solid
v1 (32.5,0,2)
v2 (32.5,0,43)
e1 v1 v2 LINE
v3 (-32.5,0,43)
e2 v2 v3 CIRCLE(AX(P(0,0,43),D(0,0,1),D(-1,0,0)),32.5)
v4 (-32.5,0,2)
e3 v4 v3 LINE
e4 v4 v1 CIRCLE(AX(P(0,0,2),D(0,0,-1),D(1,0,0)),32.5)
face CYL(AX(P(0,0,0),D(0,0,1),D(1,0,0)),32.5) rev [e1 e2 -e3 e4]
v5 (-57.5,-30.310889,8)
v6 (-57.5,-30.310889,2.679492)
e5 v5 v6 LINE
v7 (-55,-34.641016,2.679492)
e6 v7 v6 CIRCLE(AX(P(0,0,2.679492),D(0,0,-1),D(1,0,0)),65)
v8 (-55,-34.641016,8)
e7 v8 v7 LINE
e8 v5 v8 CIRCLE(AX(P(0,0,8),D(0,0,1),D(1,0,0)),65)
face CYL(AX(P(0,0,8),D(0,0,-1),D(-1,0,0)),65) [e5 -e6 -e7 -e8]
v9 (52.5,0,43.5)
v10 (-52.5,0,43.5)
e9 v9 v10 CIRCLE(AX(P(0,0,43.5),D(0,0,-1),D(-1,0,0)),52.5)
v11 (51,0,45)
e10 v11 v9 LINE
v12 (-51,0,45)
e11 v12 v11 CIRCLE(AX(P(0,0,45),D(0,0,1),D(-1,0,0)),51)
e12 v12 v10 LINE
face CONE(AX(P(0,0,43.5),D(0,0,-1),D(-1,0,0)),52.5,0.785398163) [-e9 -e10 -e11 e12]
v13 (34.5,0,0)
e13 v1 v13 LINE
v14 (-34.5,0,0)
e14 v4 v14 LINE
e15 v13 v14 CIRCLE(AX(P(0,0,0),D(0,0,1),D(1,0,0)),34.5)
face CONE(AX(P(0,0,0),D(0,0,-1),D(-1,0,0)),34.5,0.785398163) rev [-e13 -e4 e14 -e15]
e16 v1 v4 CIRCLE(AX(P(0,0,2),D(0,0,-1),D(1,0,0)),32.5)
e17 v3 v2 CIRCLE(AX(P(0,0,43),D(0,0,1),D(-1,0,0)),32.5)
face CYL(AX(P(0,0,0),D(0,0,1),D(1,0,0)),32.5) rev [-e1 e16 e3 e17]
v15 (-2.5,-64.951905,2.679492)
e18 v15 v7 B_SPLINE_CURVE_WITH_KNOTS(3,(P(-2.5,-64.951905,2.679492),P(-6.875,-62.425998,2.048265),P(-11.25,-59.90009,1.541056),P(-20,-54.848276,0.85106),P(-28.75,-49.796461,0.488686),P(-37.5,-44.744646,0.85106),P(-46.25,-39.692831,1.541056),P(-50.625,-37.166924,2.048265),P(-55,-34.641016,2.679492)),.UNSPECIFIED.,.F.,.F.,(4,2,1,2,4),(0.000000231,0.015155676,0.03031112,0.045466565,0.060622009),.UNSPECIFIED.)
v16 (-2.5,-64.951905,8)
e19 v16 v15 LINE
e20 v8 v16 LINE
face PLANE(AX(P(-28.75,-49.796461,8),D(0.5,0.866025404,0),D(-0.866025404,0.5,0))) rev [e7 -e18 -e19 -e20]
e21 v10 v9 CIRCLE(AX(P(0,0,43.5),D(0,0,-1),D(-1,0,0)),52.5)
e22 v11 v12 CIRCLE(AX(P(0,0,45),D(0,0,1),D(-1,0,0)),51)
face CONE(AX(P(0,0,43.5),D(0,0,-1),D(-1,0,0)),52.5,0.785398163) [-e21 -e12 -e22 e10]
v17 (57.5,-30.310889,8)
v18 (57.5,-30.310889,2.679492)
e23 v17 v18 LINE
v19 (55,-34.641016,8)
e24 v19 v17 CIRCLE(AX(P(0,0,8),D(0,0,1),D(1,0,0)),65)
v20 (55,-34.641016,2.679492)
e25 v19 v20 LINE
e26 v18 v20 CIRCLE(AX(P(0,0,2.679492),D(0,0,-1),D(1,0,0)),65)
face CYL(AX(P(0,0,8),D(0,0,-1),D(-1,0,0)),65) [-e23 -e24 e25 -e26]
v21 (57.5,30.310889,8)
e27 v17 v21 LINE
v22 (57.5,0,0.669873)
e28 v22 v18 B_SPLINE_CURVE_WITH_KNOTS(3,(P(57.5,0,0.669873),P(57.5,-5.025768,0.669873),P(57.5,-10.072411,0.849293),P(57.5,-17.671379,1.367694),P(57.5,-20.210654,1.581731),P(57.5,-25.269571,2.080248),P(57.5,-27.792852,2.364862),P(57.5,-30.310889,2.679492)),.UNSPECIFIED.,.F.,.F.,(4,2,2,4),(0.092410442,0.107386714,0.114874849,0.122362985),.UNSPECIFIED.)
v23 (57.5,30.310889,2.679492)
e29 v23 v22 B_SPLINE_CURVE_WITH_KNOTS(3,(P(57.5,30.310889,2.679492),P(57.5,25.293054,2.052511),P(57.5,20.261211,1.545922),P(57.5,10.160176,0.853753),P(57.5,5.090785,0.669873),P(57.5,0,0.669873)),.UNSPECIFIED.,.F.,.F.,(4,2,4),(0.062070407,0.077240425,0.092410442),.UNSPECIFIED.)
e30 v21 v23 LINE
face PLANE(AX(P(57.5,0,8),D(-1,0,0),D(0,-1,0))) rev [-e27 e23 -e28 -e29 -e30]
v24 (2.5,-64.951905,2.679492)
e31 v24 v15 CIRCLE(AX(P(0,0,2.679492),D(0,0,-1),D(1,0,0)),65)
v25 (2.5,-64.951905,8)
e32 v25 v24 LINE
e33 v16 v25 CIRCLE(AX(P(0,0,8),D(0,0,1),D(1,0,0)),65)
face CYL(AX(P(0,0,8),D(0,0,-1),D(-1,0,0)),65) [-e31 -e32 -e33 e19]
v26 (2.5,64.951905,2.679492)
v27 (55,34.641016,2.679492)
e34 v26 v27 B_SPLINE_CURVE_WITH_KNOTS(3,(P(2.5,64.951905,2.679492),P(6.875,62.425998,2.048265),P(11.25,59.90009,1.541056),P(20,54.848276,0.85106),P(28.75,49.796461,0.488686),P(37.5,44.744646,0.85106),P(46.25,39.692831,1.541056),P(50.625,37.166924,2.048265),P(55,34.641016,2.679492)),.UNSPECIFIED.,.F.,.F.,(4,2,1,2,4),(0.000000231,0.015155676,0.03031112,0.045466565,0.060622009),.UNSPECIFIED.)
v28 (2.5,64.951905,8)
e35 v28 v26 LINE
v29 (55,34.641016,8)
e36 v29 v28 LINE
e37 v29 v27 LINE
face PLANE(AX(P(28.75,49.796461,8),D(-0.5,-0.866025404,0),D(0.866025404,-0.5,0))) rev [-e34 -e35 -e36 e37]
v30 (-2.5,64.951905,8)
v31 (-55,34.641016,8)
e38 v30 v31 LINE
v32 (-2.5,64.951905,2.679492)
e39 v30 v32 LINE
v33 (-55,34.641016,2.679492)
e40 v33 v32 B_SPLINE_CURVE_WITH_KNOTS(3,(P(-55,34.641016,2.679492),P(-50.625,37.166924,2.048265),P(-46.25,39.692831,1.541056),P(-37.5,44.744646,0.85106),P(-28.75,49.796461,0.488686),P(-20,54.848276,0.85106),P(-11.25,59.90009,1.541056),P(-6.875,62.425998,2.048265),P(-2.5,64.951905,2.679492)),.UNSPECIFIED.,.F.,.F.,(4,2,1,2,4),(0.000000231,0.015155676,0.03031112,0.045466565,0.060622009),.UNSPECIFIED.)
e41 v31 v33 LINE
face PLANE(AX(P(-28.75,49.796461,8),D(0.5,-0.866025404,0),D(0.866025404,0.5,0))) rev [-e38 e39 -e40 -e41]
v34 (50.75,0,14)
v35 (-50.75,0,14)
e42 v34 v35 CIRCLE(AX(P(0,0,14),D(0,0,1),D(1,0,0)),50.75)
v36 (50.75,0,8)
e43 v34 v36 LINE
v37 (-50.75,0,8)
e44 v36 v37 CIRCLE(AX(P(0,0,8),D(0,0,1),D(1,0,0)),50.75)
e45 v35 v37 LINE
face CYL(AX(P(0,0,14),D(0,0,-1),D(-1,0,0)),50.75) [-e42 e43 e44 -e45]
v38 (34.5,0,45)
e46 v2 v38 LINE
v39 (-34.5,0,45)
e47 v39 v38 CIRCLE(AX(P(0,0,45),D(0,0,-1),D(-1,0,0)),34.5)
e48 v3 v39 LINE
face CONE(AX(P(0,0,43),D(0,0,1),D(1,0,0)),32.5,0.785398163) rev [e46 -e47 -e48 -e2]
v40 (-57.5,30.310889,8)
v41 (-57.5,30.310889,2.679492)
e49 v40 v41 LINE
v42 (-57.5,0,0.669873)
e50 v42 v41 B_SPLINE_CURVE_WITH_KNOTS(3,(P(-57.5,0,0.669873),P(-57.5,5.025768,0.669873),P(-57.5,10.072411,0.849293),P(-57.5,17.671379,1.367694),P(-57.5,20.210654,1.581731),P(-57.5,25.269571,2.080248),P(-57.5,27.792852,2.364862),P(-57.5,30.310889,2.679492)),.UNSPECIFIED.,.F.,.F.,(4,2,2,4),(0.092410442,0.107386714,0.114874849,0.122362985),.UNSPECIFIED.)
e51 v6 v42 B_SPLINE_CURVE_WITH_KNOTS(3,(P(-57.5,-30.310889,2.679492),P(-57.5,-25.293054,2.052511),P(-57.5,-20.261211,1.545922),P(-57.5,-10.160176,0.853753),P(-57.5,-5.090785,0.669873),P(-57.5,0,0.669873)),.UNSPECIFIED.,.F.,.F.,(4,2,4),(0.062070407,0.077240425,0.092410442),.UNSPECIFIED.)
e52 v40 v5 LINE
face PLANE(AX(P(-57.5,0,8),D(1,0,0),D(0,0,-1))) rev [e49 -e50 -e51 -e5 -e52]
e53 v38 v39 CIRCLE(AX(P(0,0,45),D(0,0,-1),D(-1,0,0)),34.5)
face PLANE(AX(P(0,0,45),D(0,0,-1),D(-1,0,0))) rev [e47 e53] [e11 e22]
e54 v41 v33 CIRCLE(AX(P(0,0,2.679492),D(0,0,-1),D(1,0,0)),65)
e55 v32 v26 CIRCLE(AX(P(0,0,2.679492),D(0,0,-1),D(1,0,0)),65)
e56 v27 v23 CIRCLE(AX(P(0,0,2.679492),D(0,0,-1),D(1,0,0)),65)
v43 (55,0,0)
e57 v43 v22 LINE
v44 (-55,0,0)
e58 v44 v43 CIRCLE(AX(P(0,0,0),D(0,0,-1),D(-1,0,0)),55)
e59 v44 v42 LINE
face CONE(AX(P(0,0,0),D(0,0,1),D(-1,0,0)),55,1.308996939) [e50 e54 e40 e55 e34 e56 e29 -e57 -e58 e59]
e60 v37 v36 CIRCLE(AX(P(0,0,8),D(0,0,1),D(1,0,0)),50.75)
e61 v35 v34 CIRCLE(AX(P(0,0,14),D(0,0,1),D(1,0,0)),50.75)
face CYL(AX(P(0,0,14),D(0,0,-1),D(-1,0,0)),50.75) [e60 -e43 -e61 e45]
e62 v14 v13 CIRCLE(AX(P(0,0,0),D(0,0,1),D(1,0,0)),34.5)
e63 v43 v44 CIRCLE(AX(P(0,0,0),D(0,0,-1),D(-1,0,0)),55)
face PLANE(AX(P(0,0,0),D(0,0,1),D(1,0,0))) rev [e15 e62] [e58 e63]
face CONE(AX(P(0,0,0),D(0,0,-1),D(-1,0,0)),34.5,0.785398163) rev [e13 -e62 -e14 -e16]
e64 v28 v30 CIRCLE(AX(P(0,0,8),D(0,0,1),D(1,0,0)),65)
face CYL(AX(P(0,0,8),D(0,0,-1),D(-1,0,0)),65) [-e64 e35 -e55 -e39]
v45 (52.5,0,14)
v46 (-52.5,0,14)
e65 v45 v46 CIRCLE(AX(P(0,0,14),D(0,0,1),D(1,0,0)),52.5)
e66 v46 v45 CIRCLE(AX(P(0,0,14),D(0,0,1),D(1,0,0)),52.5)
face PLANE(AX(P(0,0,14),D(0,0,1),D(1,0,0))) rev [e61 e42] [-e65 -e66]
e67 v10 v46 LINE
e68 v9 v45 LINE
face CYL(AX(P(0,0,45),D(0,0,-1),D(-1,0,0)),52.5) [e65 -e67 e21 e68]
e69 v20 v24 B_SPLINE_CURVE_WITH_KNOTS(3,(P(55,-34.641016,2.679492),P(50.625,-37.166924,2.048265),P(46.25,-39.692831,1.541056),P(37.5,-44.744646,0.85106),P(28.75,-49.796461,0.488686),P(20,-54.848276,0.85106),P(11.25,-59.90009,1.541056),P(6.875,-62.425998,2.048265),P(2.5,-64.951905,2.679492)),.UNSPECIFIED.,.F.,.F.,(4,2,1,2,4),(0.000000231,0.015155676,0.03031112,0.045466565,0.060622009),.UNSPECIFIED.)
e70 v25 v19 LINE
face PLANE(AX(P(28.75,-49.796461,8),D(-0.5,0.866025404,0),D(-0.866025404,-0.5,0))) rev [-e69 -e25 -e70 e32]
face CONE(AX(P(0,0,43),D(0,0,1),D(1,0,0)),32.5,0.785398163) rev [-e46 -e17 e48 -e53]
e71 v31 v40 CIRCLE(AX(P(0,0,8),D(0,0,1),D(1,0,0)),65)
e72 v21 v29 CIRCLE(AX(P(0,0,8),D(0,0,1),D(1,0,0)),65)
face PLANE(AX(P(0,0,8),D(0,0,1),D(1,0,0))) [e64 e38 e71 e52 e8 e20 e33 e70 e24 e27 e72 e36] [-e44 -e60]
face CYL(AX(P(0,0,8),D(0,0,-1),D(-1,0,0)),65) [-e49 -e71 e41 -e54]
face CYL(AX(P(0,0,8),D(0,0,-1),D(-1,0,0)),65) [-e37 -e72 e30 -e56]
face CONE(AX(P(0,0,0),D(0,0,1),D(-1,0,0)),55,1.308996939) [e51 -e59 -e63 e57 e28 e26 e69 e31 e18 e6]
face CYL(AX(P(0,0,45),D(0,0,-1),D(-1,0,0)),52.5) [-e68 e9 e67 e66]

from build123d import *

# Parameters (mm, degrees)
BOSS_EXTRUDE1_DEPTH = 8
SKETCH2_R           = 52.5
BOSS_EXTRUDE2_DEPTH = 45
SKETCH3_R           = 52.5
SKETCH3_R_2         = 50.75
CUT_EXTRUDE1_DEPTH  = 6
SKETCH4_R           = 32.5
CUT_EXTRUDE2_DEPTH  = 98.75607398
CHAMFER1_SIZE       = 2
CHAMFER2_SIZE       = 1.5
SKETCH5_OUTSIDE_W   = 889.986
SKETCH5_OUTSIDE_H   = 904.986
SKETCH5_OUTSIDE_R   = 55
CUT_EXTRUDE3_DEPTH  = 98.75607398
CUT_EXTRUDE3_DRAFT  = -75


with BuildPart() as part:
    # Sketch1 → Boss-Extrude1 (new body)
    with BuildSketch(Plane.XY):
        with BuildLine():
            ThreePointArc((-2.5, -64.951905284), (0, -65), (2.5, -64.951905284))
            Line((2.5, -64.951905284), (55, -34.641016151))
            ThreePointArc((55, -34.641016151), (56.291651246, -32.5), (57.5, -30.310889132))
            Line((57.5, -30.310889132), (57.5, 30.310889132))
            ThreePointArc((57.5, 30.310889132), (56.291651246, 32.5), (55, 34.641016151))
            Line((55, 34.641016151), (2.5, 64.951905284))
            ThreePointArc((2.5, 64.951905284), (0, 65), (-2.5, 64.951905284))
            Line((-2.5, 64.951905284), (-55, 34.641016151))
            ThreePointArc((-55, 34.641016151), (-56.291651246, 32.5), (-57.5, 30.310889132))
            Line((-57.5, 30.310889132), (-57.5, -30.310889132))
            ThreePointArc((-57.5, -30.310889132), (-56.291651246, -32.5), (-55, -34.641016151))
            Line((-55, -34.641016151), (-2.5, -64.951905284))
        make_face()
    extrude(amount=BOSS_EXTRUDE1_DEPTH)

    # Sketch2 → Boss-Extrude2 (add)
    with BuildSketch(Plane(origin=(0, 0, 0), x_dir=(-1, 0, 0), z_dir=(0, 0, -1))):
        Circle(SKETCH2_R)
    extrude(amount=-BOSS_EXTRUDE2_DEPTH)

    # Sketch3 → Cut-Extrude1 (cut)
    with BuildSketch(Plane.XY.offset(8)):
        with Locations(Location((0, 0, 0), (0, 0, 180))):
            Circle(SKETCH3_R)
        Circle(SKETCH3_R_2, mode=Mode.SUBTRACT)
    extrude(amount=CUT_EXTRUDE1_DEPTH, mode=Mode.SUBTRACT)

    # Sketch4 → Cut-Extrude2 (cut, through all)
    with BuildSketch(Plane.XY.offset(45)):
        Circle(SKETCH4_R)
    extrude(amount=-CUT_EXTRUDE2_DEPTH, mode=Mode.SUBTRACT)

    # Chamfer1
    chamfer1_edges = [part.edges().sort_by_distance(p)[0] for p in [
        (-32.5, 0, 0),
        (-32.5, 0, 45),
    ]]
    chamfer(chamfer1_edges, length=CHAMFER1_SIZE)

    # Chamfer2
    chamfer2_edges = [part.edges().sort_by_distance(p)[0] for p in [
        (52.5, 0, 45),
    ]]
    chamfer(chamfer2_edges, length=CHAMFER2_SIZE)


with BuildPart() as cut_extrude3_tool:
    # Sketch5 outside → Cut-Extrude3 (with draft: the straight prism first)
    with BuildSketch(Plane(origin=(0, 0, 0), x_dir=(-1, 0, 0), z_dir=(0, 0, -1))):
        Rectangle(SKETCH5_OUTSIDE_W, SKETCH5_OUTSIDE_H)
        Circle(SKETCH5_OUTSIDE_R, mode=Mode.SUBTRACT)
    extrude(amount=-CUT_EXTRUDE3_DEPTH)
    # Cut-Extrude3: the draft: its side faces are tilted about the plane it starts from
    cut_extrude3_sides = [cut_extrude3_tool.faces().sort_by_distance(p)[0] for p in [
        (0, -452.493, 49.37803699),
        (-444.993, 0, 49.37803699),
        (0, 452.493, 49.37803699),
        (444.993, 0, 49.37803699),
        (55, 0, 49.37803699),
    ]]
    draft(cut_extrude3_sides, Plane(origin=(0, 0, 0), x_dir=(-1, 0, 0), z_dir=(0, 0, -1)), CUT_EXTRUDE3_DRAFT)


with BuildPart() as part_1:
    add(part.part)

    # Cut-Extrude3: cut by cut_extrude3_tool
    add(cut_extrude3_tool.part, mode=Mode.SUBTRACT)


solid = part_1.part
